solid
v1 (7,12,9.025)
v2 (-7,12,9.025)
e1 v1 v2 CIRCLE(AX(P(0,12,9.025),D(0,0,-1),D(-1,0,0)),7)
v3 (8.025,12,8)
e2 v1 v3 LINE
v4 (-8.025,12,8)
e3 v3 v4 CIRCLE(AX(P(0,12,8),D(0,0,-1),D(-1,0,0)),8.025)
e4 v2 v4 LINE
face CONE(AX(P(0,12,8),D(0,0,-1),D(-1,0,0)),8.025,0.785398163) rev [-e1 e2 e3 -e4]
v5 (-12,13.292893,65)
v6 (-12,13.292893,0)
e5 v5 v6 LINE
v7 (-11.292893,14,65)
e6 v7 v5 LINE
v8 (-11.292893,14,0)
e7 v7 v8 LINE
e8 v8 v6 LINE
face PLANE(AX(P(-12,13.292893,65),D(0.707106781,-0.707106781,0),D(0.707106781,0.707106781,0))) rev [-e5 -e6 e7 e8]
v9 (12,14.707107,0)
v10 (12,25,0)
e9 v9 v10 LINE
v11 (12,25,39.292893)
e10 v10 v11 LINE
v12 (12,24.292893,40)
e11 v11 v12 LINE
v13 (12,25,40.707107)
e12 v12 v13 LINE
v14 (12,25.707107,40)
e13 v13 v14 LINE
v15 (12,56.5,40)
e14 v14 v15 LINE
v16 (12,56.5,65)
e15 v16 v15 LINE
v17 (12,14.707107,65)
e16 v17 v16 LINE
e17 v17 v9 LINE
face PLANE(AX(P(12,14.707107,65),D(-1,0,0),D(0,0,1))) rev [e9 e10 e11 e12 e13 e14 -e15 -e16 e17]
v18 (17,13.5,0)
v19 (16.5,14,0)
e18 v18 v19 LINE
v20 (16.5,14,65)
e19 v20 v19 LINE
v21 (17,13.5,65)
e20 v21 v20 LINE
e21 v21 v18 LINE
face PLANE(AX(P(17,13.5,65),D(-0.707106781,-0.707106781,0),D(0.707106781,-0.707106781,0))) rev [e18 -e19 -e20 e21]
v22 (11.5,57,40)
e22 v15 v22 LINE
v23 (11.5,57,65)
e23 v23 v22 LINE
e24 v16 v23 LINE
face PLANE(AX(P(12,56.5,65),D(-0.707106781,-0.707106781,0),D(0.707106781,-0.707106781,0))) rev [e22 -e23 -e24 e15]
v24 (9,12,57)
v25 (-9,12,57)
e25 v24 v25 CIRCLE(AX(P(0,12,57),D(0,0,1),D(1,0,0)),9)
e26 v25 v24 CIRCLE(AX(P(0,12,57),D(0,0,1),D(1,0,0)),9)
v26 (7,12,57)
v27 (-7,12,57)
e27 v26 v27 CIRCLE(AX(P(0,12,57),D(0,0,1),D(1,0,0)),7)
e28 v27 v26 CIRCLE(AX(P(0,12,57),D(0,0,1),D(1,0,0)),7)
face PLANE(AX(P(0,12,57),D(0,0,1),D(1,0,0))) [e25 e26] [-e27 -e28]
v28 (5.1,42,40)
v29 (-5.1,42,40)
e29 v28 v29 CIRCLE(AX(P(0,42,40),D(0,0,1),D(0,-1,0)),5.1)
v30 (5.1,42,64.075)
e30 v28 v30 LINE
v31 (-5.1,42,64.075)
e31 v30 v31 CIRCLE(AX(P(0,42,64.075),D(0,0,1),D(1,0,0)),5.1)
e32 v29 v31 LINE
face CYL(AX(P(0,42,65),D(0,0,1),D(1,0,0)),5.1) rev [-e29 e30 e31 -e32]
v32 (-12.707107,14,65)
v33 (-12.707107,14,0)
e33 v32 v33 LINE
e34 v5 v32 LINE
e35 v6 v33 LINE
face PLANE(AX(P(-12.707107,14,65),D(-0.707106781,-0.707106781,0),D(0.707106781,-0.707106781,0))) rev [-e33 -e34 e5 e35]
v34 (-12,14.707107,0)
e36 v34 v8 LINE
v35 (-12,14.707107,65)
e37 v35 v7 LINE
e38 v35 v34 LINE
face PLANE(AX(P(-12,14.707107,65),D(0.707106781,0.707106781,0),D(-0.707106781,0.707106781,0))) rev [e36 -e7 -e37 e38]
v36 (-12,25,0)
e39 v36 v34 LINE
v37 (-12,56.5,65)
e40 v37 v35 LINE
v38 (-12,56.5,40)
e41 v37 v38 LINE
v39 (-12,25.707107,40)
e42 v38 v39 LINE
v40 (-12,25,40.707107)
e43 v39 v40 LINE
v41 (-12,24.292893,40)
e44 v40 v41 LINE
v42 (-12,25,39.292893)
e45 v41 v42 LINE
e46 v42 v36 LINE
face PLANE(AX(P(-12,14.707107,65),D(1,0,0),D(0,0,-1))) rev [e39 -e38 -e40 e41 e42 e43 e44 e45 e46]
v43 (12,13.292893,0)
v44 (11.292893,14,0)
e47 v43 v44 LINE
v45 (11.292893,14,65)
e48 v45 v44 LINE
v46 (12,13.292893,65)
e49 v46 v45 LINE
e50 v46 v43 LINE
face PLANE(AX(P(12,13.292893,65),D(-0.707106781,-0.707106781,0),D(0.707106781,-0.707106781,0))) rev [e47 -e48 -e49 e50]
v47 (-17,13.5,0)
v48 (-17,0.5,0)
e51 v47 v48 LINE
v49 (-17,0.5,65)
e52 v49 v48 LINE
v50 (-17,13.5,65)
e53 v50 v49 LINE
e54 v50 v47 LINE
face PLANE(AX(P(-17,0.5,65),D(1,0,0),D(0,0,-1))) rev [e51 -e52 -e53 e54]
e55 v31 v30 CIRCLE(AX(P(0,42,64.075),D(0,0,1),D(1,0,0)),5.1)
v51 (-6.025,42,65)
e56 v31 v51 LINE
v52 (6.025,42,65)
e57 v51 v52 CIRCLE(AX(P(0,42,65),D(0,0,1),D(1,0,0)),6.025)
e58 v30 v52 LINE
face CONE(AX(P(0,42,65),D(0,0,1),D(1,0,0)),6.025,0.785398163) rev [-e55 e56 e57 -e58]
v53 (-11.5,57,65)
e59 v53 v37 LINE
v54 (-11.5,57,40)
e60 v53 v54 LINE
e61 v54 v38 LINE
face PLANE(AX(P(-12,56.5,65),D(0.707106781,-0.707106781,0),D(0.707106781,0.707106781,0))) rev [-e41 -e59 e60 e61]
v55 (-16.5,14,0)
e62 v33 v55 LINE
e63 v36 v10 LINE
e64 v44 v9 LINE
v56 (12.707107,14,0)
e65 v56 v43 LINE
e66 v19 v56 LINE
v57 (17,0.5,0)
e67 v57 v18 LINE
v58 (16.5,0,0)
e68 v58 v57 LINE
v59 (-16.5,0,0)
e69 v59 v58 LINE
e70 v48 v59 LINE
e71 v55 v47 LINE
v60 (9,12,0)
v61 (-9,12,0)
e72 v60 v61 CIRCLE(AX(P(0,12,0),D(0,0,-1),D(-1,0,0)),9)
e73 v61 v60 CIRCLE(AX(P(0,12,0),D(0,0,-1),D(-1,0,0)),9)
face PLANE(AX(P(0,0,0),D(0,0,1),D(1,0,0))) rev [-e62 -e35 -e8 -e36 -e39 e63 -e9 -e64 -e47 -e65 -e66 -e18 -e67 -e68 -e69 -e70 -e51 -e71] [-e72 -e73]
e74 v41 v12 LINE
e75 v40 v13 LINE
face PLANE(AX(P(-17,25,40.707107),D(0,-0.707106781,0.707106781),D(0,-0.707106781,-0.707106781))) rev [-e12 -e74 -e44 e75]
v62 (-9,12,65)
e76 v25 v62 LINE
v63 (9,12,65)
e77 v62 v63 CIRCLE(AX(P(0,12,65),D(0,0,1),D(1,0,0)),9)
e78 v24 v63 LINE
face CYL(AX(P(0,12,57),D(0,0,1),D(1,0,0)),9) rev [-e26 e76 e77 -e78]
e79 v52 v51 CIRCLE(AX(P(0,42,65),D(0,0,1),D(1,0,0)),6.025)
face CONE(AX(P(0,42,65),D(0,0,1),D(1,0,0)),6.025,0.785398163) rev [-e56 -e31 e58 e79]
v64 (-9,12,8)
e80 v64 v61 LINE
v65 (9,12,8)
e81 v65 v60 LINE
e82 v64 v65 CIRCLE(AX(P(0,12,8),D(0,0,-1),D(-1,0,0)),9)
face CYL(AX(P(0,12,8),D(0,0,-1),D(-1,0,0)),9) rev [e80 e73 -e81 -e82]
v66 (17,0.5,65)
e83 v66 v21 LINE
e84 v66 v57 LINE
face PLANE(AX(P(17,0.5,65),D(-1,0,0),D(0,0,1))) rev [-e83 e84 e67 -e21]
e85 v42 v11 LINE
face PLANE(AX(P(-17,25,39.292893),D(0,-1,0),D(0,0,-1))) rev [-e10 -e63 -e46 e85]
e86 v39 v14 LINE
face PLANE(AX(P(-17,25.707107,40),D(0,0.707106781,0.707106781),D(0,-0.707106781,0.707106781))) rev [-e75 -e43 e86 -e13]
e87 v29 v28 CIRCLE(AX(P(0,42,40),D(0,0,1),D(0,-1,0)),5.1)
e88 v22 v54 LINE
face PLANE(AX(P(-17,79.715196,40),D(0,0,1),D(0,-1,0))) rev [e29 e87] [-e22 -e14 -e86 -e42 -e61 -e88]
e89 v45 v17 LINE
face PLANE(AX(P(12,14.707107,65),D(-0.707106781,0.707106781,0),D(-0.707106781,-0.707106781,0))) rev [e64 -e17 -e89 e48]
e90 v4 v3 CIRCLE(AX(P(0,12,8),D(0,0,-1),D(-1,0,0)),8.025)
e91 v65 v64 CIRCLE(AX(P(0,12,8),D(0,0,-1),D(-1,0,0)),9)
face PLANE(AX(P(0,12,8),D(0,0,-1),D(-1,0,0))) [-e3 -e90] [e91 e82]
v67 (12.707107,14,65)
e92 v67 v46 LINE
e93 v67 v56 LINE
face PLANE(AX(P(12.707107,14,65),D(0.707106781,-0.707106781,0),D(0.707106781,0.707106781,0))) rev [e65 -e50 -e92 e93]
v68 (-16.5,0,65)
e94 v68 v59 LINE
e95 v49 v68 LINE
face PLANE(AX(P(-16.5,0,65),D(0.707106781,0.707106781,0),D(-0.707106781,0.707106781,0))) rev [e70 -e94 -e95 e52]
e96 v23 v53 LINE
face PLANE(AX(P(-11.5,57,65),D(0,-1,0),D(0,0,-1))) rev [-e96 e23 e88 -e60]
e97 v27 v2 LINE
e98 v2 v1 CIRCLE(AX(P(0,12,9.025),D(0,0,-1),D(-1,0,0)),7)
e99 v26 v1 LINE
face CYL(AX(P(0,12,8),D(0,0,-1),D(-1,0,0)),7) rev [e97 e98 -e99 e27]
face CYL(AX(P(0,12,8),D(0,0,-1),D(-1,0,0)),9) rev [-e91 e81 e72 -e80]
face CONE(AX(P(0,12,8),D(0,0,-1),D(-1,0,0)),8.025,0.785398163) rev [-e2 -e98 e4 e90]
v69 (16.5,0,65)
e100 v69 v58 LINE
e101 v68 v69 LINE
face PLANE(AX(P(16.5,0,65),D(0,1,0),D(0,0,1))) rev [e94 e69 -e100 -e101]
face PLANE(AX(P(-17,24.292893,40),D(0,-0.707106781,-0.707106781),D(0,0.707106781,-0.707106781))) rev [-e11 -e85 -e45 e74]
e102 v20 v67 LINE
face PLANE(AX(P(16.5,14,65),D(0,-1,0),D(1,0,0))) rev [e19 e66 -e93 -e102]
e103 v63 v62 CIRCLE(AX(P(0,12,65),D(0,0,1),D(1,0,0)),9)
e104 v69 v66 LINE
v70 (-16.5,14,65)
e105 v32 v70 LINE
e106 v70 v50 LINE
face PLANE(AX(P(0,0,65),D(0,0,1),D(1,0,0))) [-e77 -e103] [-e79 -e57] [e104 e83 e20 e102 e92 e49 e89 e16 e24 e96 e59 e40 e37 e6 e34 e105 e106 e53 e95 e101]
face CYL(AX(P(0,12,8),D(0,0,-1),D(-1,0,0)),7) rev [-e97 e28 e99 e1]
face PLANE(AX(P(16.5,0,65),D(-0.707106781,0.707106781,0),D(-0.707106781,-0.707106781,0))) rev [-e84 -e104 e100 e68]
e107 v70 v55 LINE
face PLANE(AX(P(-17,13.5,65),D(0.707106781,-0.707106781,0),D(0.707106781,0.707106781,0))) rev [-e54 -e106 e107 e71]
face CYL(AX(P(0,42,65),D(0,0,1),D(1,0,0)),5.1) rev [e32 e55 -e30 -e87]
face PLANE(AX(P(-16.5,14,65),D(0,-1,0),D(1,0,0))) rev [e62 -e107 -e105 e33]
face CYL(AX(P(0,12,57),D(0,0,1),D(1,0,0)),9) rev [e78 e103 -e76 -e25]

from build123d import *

# Parameters (mm, degrees)
BOSS_EXTRUDE1_DEPTH          = 65
CUT_EXTRUDE1_DEPTH           = 92.186621826
CUT_EXTRUDE1_DEPTH_BACK      = 92.186621826
SKETCH3_R                    = 9
CUT_EXTRUDE2_DEPTH           = 8
CUT_EXTRUDE3_START           = -8
SKETCH4_R                    = 9
CUT_EXTRUDE3_DEPTH           = 8
M16_TAPPED_HOLE1_D           = 14
M16_TAPPED_HOLE1_CSINK_D     = 16.05
M16_TAPPED_HOLE1_CSINK_ANGLE = 90
M12_TAPPED_HOLE1_D           = 10.2
M12_TAPPED_HOLE1_CSINK_D     = 12.05
M12_TAPPED_HOLE1_CSINK_ANGLE = 90


with BuildPart() as part:
    # Sketch1 → Boss-Extrude1 (new body)
    with BuildSketch(Plane.XY):
        Polygon((16.5, 0), (-16.5, 0), (-17, 0.5), (-17, 13.5), (-16.5, 14), (-12.707106781, 14), (-12, 13.292893219), (-11.292893219, 14), (-12, 14.707106781), (-12, 56.5), (-11.5, 57), (11.5, 57), (12, 56.5), (12, 14.707106781), (11.292893219, 14), (12, 13.292893219), (12.707106781, 14), (16.5, 14), (17, 13.5), (17, 0.5), align=None)
    extrude(amount=BOSS_EXTRUDE1_DEPTH)

    # Sketch2 → Cut-Extrude1 (cut, two sides: drawn at the far end of the back side and taken through both)
    with BuildSketch(Plane(origin=(12, 0, 0), x_dir=(0, 0, -1), z_dir=(1, 0, 0)).offset(-CUT_EXTRUDE1_DEPTH_BACK)):
        Polygon((-40, 79.715196203), (7.535961079, 79.715196203), (7.535961079, 25), (-39.292893219, 25), (-40, 24.292893219), (-40.707106781, 25), (-40, 25.707106781), align=None)
    extrude(amount=CUT_EXTRUDE1_DEPTH + CUT_EXTRUDE1_DEPTH_BACK, mode=Mode.SUBTRACT)

    # Sketch3 → Cut-Extrude2 (cut)
    with BuildSketch(Plane.XY.offset(65)):
        with Locations((0, 12)):
            Circle(SKETCH3_R)
    extrude(amount=-CUT_EXTRUDE2_DEPTH, mode=Mode.SUBTRACT)

    # Sketch4 → Cut-Extrude3 (cut)
    with BuildSketch(Plane(origin=(0, 0, 0), x_dir=(-1, 0, 0), z_dir=(0, 0, -1)).offset(CUT_EXTRUDE3_START)):
        with Locations(Location((0, 12, 0), (0, 0, 180))):
            Circle(SKETCH4_R)
    extrude(amount=CUT_EXTRUDE3_DEPTH, mode=Mode.SUBTRACT)

    # M16 Tapped Hole1 (through all)
    with Locations(Plane(origin=(0, 12, 8), x_dir=(-1, 0, 0), z_dir=(0, 0, -1))):
        with Locations((0, 0)):
            CounterSinkHole(M16_TAPPED_HOLE1_D / 2, M16_TAPPED_HOLE1_CSINK_D / 2, counter_sink_angle=M16_TAPPED_HOLE1_CSINK_ANGLE)

    # M12 Tapped Hole1 (through all)
    with Locations(Plane(origin=(0, 42, 65), x_dir=(1, 0, 0), z_dir=(0, 0, 1))):
        with Locations((0, 0)):
            CounterSinkHole(M12_TAPPED_HOLE1_D / 2, M12_TAPPED_HOLE1_CSINK_D / 2, counter_sink_angle=M12_TAPPED_HOLE1_CSINK_ANGLE)


solid = part.part
